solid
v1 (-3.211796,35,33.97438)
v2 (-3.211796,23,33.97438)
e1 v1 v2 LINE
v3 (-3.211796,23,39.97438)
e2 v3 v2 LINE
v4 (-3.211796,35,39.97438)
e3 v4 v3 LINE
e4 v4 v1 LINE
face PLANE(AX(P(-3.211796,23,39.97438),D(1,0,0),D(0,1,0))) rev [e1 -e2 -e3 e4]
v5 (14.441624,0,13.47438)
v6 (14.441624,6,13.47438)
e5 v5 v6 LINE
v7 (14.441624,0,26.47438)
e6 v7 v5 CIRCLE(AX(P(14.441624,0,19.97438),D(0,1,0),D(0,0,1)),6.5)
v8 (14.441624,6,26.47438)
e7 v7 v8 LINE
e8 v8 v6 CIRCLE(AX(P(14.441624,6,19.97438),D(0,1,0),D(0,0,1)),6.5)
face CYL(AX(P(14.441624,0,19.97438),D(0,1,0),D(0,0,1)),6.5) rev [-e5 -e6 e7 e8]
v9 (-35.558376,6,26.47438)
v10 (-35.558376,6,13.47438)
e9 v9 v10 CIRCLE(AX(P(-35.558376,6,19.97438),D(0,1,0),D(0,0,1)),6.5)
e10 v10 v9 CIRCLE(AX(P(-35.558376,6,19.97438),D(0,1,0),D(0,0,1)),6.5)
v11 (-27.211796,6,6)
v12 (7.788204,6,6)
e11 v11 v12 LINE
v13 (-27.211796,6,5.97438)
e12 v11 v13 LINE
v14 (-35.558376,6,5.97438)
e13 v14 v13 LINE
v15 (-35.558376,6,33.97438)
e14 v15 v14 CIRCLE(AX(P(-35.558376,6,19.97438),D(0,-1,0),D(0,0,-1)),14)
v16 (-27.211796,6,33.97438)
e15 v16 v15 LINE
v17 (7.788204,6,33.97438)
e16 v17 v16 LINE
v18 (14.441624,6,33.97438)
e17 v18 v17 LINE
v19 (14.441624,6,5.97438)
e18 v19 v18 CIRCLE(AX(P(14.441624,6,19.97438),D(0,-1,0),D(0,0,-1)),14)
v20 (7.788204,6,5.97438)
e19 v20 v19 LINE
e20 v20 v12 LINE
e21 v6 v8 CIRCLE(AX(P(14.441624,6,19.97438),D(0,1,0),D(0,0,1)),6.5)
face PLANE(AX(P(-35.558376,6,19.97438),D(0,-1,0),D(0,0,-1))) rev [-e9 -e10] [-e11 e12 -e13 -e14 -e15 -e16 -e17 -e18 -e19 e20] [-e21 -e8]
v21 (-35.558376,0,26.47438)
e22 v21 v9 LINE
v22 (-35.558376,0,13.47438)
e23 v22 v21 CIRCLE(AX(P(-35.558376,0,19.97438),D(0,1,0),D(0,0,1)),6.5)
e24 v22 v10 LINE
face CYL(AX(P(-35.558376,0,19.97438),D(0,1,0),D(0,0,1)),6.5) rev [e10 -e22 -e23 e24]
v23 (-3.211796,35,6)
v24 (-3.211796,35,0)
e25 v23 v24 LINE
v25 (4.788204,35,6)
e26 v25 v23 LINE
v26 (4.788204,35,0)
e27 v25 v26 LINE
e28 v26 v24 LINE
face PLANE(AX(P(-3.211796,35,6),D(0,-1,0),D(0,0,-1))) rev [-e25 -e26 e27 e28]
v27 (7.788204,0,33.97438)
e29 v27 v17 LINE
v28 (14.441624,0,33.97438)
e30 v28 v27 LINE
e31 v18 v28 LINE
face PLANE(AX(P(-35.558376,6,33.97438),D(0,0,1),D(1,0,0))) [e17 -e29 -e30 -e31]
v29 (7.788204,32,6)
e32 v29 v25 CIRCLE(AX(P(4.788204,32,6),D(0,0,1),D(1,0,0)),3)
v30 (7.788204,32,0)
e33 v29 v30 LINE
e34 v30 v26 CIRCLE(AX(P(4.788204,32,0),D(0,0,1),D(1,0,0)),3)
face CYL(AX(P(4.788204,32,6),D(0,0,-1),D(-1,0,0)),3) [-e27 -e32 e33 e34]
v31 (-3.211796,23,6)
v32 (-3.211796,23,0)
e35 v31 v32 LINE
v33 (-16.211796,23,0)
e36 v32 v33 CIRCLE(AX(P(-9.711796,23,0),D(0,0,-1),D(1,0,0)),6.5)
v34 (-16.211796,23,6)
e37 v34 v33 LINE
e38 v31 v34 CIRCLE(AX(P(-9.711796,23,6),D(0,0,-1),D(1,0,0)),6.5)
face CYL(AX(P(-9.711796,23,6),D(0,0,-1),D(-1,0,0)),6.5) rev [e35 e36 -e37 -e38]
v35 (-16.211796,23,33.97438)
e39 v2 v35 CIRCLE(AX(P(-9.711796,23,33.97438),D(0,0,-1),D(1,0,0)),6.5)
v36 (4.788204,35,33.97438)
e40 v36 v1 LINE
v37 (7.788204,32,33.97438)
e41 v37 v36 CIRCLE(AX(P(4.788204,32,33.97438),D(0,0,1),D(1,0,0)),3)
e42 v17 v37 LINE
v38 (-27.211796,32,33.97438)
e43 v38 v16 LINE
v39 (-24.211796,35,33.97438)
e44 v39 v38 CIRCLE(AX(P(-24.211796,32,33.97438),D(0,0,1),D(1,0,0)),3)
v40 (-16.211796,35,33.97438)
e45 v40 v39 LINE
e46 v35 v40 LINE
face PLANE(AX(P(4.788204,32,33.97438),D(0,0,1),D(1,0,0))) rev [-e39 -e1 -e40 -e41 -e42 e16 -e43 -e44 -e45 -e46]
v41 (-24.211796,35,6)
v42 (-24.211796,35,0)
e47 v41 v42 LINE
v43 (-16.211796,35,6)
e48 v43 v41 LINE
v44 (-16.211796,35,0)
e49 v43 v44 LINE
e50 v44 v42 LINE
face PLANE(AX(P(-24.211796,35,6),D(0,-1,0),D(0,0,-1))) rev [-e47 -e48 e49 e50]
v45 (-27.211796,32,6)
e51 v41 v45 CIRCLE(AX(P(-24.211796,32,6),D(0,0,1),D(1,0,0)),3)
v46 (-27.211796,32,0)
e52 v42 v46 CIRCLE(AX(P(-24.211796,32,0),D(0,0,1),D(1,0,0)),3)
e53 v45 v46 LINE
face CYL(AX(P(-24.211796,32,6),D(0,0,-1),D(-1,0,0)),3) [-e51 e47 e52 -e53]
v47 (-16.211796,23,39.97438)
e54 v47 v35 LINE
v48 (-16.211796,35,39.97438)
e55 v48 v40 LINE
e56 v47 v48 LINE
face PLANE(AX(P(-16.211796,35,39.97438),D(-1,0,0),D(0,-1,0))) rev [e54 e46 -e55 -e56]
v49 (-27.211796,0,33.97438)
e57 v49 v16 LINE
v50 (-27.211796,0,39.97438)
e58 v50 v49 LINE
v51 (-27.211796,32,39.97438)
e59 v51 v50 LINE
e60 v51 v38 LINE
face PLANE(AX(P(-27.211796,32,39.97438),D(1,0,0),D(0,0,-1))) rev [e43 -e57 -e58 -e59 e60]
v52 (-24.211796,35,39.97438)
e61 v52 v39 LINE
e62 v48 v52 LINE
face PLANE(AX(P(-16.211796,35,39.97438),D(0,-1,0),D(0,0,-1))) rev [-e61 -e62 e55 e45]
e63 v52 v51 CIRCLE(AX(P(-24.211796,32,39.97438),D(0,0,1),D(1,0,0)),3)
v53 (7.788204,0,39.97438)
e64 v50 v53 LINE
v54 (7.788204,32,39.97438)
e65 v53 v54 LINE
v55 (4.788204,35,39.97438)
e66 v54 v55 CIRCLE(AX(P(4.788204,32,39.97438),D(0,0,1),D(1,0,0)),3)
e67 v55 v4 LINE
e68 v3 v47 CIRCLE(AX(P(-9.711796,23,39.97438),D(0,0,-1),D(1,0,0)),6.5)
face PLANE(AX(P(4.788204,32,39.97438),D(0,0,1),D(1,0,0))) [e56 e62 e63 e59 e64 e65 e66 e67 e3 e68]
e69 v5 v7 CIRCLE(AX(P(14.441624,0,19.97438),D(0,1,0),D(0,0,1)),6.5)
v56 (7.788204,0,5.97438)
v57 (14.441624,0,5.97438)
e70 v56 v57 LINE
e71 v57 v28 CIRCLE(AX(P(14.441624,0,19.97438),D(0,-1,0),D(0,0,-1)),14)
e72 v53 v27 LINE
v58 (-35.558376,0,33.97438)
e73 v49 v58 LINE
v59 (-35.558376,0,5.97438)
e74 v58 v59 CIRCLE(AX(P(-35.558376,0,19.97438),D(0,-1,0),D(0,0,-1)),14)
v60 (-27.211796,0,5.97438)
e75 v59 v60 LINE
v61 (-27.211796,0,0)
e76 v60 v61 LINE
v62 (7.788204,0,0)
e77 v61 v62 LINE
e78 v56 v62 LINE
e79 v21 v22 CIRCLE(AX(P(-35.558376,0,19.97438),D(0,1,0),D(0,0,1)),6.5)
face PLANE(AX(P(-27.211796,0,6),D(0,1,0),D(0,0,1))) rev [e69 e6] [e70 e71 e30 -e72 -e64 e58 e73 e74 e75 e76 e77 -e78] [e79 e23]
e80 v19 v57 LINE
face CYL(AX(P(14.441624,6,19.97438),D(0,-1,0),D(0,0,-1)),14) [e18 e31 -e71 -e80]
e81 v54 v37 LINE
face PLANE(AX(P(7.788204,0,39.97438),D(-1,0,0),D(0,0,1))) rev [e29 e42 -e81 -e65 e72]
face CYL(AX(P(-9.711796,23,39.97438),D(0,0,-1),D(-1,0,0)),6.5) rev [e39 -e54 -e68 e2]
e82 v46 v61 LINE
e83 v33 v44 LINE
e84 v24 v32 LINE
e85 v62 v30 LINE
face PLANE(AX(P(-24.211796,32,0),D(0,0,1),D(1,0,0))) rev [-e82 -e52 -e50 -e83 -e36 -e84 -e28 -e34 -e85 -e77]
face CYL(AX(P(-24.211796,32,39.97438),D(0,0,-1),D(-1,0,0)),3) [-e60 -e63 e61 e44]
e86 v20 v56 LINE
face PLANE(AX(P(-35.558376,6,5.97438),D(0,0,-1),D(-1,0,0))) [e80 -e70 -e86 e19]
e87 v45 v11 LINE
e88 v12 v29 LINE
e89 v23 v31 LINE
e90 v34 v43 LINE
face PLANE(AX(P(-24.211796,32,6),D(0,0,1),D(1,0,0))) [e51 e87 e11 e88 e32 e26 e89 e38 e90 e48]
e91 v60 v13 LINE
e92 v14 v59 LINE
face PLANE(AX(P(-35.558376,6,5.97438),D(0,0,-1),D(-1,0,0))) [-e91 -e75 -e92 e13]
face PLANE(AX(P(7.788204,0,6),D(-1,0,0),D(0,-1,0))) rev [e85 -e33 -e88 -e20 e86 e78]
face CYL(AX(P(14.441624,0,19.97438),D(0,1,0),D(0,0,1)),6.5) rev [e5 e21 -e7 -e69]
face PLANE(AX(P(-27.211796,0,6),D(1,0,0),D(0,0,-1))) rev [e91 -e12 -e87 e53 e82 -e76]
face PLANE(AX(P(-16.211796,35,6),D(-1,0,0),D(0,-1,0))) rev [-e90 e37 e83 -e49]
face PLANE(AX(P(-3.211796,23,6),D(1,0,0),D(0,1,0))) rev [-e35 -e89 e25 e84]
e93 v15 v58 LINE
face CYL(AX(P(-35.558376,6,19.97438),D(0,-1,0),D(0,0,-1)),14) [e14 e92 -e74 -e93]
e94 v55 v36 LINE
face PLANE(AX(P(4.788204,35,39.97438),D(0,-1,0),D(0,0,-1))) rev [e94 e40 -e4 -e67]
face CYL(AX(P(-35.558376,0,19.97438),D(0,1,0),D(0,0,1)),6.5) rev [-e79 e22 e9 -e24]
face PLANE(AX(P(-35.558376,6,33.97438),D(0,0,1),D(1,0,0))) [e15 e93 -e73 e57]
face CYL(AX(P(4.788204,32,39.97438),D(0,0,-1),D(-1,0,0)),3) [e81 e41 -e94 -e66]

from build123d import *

# Parameters (mm, degrees)
CLEVIS_EAR_1_DEPTH         = 6
BASE_PLATE_DEPTH           = 6
MOUNTING_HOLES_SKETCH_R    = 6.5
MOUNTING_HOLES_2X_13_DEPTH = 67.717997207
CLEVIS_EAR_2_DEPTH         = 6


with BuildPart() as part:
    # Clevis Ear 1 Sketch → Clevis Ear 1 (new body)
    with BuildSketch(Plane.XY):
        with BuildLine():
            Line((-27.211796247, 0), (7.788203753, 0))
            Line((7.788203753, 0), (7.788203753, 32))
            ThreePointArc((7.788203753, 32), (6.909524097, 34.121320344), (4.788203753, 35))
            Line((4.788203753, 35), (-3.211796247, 35))
            Line((-3.211796247, 35), (-3.211796247, 23))
            ThreePointArc((-3.211796247, 23), (-9.711796247, 16.5), (-16.211796247, 23))
            Line((-16.211796247, 23), (-16.211796247, 35))
            Line((-16.211796247, 35), (-24.211796247, 35))
            ThreePointArc((-24.211796247, 35), (-26.33311659, 34.121320344), (-27.211796247, 32))
            Line((-27.211796247, 32), (-27.211796247, 0))
        make_face()
    extrude(amount=CLEVIS_EAR_1_DEPTH)

    # Base Plate Sketch → Base Plate (add)
    with BuildSketch(Plane.XZ):
        with BuildLine():
            Line((-35.558376082, 5.974380222), (14.441623918, 5.974380222))
            ThreePointArc((14.441623918, 5.974380222), (28.441623918, 19.974380222), (14.441623918, 33.974380222))
            Line((14.441623918, 33.974380222), (-35.558376082, 33.974380222))
            ThreePointArc((-35.558376082, 33.974380222), (-49.558376082, 19.974380222), (-35.558376082, 5.974380222))
        make_face()
    extrude(amount=-BASE_PLATE_DEPTH)

    # Mounting Holes Sketch → Mounting Holes 2xØ13 (cut, through all)
    with BuildSketch(Plane(origin=(0, 6, 0), x_dir=(1, 0, 0), z_dir=(0, 1, 0))):
        with Locations(Location((-35.558376082, -19.974380222, 0), (0, 0, 270))):
            Circle(MOUNTING_HOLES_SKETCH_R)
        with Locations(Location((14.441623918, -19.974380222, 0), (0, 0, 270))):
            Circle(MOUNTING_HOLES_SKETCH_R)
    extrude(amount=-MOUNTING_HOLES_2X_13_DEPTH, mode=Mode.SUBTRACT)

    # Clevis Ear 2 Sketch → Clevis Ear 2 (add)
    with BuildSketch(Plane.XY.offset(33.974380222)):
        with BuildLine():
            Line((-27.211796247, 0), (7.788203753, 0))
            Line((7.788203753, 0), (7.788203753, 32))
            ThreePointArc((7.788203753, 32), (6.909524097, 34.121320344), (4.788203753, 35))
            Line((4.788203753, 35), (-3.211796247, 35))
            Line((-3.211796247, 35), (-3.211796247, 23))
            ThreePointArc((-3.211796247, 23), (-9.711796247, 16.5), (-16.211796247, 23))
            Line((-16.211796247, 23), (-16.211796247, 35))
            Line((-16.211796247, 35), (-24.211796247, 35))
            ThreePointArc((-24.211796247, 35), (-26.33311659, 34.121320344), (-27.211796247, 32))
            Line((-27.211796247, 32), (-27.211796247, 0))
        make_face()
    extrude(amount=CLEVIS_EAR_2_DEPTH)


solid = part.part
